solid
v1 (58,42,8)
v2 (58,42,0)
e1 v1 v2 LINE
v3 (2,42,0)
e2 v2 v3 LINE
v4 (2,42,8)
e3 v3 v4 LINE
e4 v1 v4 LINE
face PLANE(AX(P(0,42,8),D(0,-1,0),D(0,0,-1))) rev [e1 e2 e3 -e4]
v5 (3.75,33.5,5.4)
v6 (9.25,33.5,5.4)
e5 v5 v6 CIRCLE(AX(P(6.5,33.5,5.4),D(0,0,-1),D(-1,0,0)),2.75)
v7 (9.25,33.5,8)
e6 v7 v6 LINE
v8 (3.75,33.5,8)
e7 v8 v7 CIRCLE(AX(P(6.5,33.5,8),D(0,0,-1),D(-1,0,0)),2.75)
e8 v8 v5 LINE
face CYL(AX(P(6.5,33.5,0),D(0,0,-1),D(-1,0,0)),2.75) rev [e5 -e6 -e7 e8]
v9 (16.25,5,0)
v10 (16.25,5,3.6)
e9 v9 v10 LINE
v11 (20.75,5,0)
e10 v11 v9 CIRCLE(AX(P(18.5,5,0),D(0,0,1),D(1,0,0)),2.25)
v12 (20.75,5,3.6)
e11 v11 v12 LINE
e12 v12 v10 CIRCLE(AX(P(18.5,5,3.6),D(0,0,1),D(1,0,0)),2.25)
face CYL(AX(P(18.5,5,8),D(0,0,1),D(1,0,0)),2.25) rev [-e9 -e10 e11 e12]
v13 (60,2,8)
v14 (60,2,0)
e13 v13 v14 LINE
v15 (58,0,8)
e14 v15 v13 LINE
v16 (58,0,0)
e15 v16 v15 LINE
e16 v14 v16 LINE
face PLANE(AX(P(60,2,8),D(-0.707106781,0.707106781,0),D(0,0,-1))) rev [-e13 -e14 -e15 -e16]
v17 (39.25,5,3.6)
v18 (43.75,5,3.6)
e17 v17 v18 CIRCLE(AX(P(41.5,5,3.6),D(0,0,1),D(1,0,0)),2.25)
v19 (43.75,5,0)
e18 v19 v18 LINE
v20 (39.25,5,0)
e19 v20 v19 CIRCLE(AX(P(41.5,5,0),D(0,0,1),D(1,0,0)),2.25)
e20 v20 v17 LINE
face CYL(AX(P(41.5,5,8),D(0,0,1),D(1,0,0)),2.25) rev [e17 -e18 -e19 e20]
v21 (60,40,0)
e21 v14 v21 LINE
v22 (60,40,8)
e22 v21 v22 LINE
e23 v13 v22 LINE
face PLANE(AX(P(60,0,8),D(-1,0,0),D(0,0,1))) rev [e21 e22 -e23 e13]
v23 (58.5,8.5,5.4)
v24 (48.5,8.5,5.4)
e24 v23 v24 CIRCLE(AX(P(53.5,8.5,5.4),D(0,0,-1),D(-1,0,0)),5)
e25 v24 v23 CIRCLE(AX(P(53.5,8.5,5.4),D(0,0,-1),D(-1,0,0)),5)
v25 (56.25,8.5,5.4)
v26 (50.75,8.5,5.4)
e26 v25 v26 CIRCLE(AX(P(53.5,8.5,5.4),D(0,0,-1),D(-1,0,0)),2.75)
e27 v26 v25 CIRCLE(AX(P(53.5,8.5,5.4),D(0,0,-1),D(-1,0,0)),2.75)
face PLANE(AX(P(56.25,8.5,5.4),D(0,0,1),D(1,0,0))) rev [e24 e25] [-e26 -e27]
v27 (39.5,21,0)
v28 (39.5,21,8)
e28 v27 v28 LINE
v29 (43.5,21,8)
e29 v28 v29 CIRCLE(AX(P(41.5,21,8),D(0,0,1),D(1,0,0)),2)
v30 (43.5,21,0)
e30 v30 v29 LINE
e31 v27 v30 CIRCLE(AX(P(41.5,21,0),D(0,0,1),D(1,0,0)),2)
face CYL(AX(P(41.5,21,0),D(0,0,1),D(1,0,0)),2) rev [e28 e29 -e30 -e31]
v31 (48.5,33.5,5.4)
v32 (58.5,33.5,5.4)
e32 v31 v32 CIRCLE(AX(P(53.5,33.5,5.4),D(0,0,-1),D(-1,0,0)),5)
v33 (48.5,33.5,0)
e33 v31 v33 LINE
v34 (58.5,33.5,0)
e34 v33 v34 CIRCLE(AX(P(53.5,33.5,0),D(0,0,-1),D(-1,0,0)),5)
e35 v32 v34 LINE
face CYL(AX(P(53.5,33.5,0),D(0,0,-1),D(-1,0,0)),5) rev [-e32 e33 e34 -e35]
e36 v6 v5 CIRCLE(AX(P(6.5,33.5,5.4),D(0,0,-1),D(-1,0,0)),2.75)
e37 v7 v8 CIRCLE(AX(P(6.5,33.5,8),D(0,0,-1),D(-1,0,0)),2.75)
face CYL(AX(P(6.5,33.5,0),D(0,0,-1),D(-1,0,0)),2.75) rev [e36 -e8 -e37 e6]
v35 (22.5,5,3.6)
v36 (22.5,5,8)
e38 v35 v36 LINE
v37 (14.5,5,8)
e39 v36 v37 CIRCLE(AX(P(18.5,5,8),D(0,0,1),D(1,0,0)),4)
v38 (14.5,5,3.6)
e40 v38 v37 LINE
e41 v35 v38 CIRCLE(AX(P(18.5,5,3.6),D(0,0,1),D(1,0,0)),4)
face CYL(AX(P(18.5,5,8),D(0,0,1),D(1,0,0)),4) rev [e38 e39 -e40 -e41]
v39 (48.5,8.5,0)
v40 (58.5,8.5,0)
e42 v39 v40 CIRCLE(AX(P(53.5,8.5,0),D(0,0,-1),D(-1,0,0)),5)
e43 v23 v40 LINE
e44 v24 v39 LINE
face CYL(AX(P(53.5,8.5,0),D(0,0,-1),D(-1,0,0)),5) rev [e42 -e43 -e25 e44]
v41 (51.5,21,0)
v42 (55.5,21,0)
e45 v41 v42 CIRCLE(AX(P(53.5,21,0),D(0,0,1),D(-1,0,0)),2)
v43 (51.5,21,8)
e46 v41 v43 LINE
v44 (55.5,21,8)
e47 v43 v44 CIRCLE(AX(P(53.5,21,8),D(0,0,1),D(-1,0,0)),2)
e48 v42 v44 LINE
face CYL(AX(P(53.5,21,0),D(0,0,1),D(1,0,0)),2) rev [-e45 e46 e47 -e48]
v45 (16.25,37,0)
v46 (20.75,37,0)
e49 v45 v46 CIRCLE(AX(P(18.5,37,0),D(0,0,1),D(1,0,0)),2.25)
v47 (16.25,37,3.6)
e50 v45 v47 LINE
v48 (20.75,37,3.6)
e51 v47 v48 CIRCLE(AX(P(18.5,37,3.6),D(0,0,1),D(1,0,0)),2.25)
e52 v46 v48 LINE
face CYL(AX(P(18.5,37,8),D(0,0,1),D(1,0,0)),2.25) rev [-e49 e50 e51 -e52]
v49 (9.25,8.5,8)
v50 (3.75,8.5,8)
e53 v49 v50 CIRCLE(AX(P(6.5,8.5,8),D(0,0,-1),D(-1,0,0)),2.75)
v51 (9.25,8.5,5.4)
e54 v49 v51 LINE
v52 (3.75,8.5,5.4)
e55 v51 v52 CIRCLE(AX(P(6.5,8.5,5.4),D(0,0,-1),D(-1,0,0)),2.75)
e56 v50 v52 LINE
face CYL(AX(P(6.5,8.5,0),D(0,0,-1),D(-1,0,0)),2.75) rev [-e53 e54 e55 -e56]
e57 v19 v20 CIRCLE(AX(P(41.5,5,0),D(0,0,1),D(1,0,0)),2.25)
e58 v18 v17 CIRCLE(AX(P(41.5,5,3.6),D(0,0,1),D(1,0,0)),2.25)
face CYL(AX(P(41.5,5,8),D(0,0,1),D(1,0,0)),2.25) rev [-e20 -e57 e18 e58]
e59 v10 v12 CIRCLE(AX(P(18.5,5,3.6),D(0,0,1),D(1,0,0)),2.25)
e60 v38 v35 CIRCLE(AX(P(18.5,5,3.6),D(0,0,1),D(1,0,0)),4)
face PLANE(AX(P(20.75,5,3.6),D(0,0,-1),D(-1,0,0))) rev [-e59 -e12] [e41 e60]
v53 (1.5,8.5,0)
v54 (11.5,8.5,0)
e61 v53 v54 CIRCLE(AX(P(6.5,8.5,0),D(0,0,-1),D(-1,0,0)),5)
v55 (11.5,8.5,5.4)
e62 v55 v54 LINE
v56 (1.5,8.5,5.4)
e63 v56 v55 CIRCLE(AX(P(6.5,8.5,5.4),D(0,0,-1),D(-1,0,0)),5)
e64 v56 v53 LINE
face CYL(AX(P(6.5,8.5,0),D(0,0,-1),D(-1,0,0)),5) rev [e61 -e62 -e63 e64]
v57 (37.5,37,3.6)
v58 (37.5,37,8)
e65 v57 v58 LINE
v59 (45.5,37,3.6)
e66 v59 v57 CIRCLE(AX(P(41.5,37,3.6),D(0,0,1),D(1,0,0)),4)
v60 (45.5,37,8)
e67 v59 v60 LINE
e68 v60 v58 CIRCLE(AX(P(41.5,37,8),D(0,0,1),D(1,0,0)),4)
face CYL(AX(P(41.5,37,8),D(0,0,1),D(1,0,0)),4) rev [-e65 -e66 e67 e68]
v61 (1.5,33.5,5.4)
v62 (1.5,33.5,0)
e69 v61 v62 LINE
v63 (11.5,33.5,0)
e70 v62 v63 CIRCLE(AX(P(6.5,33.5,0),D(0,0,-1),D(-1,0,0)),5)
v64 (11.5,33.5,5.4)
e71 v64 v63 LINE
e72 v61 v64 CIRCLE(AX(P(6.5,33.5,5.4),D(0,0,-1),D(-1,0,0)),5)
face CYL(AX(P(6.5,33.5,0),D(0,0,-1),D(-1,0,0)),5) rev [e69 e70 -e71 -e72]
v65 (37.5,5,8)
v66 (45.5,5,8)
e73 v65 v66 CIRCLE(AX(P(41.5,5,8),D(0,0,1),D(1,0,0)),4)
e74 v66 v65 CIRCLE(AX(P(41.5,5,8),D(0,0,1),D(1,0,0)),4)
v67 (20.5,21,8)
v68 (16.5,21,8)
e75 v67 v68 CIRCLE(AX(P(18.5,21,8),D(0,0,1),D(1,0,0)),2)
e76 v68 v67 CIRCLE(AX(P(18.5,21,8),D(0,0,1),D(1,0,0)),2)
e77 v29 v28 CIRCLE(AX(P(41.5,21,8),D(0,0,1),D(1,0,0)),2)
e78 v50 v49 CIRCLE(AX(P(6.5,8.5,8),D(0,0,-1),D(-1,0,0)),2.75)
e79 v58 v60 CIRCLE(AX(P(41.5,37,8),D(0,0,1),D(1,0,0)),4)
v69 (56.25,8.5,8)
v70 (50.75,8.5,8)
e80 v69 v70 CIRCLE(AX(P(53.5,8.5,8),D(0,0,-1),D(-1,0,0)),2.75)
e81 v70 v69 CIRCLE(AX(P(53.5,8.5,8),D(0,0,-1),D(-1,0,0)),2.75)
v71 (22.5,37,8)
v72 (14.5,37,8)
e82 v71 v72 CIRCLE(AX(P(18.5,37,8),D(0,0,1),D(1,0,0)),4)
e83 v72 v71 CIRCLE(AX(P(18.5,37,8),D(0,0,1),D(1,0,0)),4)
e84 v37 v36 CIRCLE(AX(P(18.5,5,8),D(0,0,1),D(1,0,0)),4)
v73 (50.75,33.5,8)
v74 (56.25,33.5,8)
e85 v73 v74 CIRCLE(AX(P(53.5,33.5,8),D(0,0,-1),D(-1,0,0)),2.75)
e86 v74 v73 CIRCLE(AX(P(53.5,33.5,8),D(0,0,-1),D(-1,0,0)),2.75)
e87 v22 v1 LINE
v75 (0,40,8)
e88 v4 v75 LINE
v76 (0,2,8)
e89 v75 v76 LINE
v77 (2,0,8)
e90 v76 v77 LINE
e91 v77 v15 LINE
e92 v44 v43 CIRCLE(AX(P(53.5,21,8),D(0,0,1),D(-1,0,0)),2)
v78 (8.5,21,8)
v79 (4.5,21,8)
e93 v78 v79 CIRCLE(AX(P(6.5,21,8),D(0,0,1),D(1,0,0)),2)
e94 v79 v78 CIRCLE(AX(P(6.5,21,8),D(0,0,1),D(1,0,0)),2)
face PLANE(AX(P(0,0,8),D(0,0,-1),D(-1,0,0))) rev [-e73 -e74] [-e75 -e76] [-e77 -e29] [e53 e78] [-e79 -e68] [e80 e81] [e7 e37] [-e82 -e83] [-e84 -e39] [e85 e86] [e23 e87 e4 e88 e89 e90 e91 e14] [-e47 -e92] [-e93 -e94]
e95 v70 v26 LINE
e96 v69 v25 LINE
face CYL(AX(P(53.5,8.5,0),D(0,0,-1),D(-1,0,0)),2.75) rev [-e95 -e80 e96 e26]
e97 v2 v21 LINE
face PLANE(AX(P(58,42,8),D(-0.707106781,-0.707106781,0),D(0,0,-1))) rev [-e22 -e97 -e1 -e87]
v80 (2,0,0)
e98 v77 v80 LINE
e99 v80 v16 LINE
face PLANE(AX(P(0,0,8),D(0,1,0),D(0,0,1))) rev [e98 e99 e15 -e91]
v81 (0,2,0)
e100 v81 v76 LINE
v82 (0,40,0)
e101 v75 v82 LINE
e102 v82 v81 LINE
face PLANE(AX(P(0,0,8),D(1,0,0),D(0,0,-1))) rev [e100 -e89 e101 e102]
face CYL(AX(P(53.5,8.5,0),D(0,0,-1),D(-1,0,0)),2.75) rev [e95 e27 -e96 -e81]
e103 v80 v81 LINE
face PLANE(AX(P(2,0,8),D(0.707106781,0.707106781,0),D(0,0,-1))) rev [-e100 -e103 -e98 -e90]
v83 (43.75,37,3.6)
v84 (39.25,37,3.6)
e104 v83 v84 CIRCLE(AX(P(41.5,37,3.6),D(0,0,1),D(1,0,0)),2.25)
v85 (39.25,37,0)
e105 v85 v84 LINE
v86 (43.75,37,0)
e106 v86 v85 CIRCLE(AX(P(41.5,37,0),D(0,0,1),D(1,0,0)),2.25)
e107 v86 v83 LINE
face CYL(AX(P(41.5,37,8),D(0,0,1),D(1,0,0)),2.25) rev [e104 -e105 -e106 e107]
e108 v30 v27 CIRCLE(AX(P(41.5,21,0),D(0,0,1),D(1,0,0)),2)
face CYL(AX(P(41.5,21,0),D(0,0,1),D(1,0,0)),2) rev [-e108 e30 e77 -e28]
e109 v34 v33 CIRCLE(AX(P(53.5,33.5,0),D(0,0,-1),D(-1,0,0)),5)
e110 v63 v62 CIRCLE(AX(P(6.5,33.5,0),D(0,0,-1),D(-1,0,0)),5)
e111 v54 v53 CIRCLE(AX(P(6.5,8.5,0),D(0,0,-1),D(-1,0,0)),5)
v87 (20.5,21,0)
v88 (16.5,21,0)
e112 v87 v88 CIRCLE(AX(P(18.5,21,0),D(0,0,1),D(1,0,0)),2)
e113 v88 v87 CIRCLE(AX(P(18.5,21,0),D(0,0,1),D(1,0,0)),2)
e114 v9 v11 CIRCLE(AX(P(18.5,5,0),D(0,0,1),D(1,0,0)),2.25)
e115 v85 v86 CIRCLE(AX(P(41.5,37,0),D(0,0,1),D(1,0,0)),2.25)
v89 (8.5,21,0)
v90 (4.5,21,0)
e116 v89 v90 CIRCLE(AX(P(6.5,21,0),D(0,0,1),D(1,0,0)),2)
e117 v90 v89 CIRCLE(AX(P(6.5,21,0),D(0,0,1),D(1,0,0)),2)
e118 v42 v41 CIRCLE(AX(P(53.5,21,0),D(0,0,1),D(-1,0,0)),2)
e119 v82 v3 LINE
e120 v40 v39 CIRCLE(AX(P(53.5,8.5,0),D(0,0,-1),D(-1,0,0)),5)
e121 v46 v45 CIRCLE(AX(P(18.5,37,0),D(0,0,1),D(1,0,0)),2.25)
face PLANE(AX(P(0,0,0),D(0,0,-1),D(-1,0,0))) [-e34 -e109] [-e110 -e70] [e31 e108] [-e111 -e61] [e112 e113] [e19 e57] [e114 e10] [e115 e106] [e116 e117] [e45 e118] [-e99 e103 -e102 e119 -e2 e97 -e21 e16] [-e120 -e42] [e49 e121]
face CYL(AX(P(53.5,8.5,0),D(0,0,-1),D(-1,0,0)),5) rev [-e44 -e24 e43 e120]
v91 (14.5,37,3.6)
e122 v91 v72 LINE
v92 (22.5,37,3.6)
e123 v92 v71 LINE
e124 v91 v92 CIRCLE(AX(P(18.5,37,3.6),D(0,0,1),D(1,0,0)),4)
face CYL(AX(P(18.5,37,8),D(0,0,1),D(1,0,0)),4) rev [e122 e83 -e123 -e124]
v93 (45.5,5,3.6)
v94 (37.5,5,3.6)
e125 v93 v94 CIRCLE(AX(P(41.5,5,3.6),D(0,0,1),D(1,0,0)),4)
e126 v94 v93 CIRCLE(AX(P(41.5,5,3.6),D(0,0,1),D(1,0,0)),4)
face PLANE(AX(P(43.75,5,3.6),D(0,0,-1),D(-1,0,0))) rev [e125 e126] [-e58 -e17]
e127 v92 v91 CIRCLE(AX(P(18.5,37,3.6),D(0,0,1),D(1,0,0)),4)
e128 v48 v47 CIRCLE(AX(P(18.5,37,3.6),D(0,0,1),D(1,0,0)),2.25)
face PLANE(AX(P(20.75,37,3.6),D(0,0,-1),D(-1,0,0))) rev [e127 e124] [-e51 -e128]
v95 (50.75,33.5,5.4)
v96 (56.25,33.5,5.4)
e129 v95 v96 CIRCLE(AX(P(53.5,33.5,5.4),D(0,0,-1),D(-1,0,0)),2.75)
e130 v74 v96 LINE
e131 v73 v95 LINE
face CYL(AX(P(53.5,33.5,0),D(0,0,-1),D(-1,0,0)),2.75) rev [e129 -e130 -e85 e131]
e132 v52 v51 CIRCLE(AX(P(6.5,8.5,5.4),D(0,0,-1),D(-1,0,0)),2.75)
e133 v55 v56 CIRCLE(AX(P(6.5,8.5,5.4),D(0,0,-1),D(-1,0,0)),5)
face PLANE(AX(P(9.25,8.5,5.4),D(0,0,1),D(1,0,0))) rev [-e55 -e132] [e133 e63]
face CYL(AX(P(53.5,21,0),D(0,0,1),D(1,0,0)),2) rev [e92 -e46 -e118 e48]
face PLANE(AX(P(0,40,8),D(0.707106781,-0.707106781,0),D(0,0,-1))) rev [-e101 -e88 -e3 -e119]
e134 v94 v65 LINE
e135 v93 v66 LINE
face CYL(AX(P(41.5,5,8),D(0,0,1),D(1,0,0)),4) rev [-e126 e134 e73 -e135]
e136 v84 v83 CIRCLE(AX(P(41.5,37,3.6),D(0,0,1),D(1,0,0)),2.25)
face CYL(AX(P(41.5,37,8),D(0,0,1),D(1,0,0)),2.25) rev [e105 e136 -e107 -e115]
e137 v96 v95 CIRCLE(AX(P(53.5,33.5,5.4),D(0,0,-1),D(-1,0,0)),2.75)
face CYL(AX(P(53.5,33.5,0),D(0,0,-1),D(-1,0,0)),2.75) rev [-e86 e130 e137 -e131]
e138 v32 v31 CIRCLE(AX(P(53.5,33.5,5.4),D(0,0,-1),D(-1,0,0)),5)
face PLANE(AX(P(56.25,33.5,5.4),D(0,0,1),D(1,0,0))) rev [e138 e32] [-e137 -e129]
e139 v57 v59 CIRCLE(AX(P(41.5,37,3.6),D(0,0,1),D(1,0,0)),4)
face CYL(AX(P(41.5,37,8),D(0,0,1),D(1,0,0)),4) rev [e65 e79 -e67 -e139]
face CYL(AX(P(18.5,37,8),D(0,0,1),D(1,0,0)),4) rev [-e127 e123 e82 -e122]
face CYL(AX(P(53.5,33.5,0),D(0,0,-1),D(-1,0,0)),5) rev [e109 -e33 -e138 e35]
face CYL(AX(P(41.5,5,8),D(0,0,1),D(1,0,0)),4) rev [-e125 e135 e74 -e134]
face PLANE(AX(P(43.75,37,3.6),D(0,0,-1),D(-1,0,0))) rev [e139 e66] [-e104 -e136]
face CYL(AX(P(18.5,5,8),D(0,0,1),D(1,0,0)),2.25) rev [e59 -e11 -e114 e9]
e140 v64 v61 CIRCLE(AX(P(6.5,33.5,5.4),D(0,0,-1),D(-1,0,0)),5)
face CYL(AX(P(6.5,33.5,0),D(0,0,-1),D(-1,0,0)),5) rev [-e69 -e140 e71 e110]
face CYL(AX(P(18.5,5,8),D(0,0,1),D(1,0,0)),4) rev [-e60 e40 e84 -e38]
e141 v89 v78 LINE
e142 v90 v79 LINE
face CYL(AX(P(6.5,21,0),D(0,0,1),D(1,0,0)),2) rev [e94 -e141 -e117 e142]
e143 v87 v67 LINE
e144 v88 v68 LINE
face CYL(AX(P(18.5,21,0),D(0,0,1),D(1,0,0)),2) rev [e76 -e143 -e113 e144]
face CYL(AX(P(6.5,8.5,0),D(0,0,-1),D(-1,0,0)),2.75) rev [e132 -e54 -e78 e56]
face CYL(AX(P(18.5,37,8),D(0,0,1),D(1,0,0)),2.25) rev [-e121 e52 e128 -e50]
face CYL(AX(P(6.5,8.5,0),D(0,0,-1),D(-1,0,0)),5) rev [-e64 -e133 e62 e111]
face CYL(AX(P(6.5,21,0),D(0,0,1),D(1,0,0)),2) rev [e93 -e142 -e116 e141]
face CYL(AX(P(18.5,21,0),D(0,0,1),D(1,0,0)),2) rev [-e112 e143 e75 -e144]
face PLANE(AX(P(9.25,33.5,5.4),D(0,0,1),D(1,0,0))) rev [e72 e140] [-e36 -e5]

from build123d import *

# Parameters (mm, degrees)
SKETCH1_W                                           = 60
SKETCH1_H                                           = 42
BOSS_EXTRUDE1_DEPTH                                 = 8
CBORE_FOR_M4_HEX_SOCKET_HEAD_CAP_SCREW2_D           = 4.5
CBORE_FOR_M4_HEX_SOCKET_HEAD_CAP_SCREW2_CBORE_D     = 8
CBORE_FOR_M4_HEX_SOCKET_HEAD_CAP_SCREW2_CBORE_DEPTH = 4.4
SKETCH4_R                                           = 2
CUT_EXTRUDE1_DEPTH                                  = 74.674961826
CBORE_FOR_M5_HEX_SOCKET_HEAD_CAP_SCREW1_D           = 5.5
CBORE_FOR_M5_HEX_SOCKET_HEAD_CAP_SCREW1_CBORE_D     = 10
CBORE_FOR_M5_HEX_SOCKET_HEAD_CAP_SCREW1_CBORE_DEPTH = 5.4
SKETCH7_R                                           = 2
CUT_EXTRUDE2_DEPTH                                  = 74.674961826
CHAMFER1_SIZE                                       = 2


with BuildPart() as part:
    # Sketch1 → Boss-Extrude1 (new body)
    with BuildSketch(Plane.XY):
        with Locations((30, 21)):
            Rectangle(SKETCH1_W, SKETCH1_H)
    extrude(amount=BOSS_EXTRUDE1_DEPTH)

    # CBORE for M4 Hex Socket Head Cap Screw2 (through all)
    with Locations(Plane.XY.offset(8)):
        with Locations((41.5, 37), (18.5, 37), (18.5, 5), (41.5, 5)):
            CounterBoreHole(CBORE_FOR_M4_HEX_SOCKET_HEAD_CAP_SCREW2_D / 2, CBORE_FOR_M4_HEX_SOCKET_HEAD_CAP_SCREW2_CBORE_D / 2, CBORE_FOR_M4_HEX_SOCKET_HEAD_CAP_SCREW2_CBORE_DEPTH)

    # Sketch4 → Cut-Extrude1 (cut, through all)
    with BuildSketch(Plane.XY.offset(8)):
        with Locations((18.5, 21)):
            Circle(SKETCH4_R)
        with Locations((41.5, 21)):
            Circle(SKETCH4_R)
    extrude(amount=-CUT_EXTRUDE1_DEPTH, mode=Mode.SUBTRACT)

    # CBORE for M5 Hex Socket Head Cap Screw1 (through all)
    with Locations(Plane(origin=(0, 0, 0), x_dir=(1, 0, 0), z_dir=(0, 0, -1))):
        with Locations((53.5, -33.5), (6.5, -33.5), (6.5, -8.5), (53.5, -8.5)):
            CounterBoreHole(CBORE_FOR_M5_HEX_SOCKET_HEAD_CAP_SCREW1_D / 2, CBORE_FOR_M5_HEX_SOCKET_HEAD_CAP_SCREW1_CBORE_D / 2, CBORE_FOR_M5_HEX_SOCKET_HEAD_CAP_SCREW1_CBORE_DEPTH)

    # Sketch7 → Cut-Extrude2 (cut, through all)
    with BuildSketch(Plane.XY.offset(8)):
        with Locations((6.5, 21)):
            Circle(SKETCH7_R)
        with Locations(Location((53.5, 21, 0), (0, 0, 180))):
            Circle(SKETCH7_R)
    extrude(amount=-CUT_EXTRUDE2_DEPTH, mode=Mode.SUBTRACT)

    # Chamfer1
    chamfer1_edges = [part.edges().sort_by_distance(p)[0] for p in [
        (0, 42, 4),
        (60, 42, 4),
        (60, 0, 4),
        (0, 0, 4),
    ]]
    chamfer(chamfer1_edges, length=CHAMFER1_SIZE)


solid = part.part
